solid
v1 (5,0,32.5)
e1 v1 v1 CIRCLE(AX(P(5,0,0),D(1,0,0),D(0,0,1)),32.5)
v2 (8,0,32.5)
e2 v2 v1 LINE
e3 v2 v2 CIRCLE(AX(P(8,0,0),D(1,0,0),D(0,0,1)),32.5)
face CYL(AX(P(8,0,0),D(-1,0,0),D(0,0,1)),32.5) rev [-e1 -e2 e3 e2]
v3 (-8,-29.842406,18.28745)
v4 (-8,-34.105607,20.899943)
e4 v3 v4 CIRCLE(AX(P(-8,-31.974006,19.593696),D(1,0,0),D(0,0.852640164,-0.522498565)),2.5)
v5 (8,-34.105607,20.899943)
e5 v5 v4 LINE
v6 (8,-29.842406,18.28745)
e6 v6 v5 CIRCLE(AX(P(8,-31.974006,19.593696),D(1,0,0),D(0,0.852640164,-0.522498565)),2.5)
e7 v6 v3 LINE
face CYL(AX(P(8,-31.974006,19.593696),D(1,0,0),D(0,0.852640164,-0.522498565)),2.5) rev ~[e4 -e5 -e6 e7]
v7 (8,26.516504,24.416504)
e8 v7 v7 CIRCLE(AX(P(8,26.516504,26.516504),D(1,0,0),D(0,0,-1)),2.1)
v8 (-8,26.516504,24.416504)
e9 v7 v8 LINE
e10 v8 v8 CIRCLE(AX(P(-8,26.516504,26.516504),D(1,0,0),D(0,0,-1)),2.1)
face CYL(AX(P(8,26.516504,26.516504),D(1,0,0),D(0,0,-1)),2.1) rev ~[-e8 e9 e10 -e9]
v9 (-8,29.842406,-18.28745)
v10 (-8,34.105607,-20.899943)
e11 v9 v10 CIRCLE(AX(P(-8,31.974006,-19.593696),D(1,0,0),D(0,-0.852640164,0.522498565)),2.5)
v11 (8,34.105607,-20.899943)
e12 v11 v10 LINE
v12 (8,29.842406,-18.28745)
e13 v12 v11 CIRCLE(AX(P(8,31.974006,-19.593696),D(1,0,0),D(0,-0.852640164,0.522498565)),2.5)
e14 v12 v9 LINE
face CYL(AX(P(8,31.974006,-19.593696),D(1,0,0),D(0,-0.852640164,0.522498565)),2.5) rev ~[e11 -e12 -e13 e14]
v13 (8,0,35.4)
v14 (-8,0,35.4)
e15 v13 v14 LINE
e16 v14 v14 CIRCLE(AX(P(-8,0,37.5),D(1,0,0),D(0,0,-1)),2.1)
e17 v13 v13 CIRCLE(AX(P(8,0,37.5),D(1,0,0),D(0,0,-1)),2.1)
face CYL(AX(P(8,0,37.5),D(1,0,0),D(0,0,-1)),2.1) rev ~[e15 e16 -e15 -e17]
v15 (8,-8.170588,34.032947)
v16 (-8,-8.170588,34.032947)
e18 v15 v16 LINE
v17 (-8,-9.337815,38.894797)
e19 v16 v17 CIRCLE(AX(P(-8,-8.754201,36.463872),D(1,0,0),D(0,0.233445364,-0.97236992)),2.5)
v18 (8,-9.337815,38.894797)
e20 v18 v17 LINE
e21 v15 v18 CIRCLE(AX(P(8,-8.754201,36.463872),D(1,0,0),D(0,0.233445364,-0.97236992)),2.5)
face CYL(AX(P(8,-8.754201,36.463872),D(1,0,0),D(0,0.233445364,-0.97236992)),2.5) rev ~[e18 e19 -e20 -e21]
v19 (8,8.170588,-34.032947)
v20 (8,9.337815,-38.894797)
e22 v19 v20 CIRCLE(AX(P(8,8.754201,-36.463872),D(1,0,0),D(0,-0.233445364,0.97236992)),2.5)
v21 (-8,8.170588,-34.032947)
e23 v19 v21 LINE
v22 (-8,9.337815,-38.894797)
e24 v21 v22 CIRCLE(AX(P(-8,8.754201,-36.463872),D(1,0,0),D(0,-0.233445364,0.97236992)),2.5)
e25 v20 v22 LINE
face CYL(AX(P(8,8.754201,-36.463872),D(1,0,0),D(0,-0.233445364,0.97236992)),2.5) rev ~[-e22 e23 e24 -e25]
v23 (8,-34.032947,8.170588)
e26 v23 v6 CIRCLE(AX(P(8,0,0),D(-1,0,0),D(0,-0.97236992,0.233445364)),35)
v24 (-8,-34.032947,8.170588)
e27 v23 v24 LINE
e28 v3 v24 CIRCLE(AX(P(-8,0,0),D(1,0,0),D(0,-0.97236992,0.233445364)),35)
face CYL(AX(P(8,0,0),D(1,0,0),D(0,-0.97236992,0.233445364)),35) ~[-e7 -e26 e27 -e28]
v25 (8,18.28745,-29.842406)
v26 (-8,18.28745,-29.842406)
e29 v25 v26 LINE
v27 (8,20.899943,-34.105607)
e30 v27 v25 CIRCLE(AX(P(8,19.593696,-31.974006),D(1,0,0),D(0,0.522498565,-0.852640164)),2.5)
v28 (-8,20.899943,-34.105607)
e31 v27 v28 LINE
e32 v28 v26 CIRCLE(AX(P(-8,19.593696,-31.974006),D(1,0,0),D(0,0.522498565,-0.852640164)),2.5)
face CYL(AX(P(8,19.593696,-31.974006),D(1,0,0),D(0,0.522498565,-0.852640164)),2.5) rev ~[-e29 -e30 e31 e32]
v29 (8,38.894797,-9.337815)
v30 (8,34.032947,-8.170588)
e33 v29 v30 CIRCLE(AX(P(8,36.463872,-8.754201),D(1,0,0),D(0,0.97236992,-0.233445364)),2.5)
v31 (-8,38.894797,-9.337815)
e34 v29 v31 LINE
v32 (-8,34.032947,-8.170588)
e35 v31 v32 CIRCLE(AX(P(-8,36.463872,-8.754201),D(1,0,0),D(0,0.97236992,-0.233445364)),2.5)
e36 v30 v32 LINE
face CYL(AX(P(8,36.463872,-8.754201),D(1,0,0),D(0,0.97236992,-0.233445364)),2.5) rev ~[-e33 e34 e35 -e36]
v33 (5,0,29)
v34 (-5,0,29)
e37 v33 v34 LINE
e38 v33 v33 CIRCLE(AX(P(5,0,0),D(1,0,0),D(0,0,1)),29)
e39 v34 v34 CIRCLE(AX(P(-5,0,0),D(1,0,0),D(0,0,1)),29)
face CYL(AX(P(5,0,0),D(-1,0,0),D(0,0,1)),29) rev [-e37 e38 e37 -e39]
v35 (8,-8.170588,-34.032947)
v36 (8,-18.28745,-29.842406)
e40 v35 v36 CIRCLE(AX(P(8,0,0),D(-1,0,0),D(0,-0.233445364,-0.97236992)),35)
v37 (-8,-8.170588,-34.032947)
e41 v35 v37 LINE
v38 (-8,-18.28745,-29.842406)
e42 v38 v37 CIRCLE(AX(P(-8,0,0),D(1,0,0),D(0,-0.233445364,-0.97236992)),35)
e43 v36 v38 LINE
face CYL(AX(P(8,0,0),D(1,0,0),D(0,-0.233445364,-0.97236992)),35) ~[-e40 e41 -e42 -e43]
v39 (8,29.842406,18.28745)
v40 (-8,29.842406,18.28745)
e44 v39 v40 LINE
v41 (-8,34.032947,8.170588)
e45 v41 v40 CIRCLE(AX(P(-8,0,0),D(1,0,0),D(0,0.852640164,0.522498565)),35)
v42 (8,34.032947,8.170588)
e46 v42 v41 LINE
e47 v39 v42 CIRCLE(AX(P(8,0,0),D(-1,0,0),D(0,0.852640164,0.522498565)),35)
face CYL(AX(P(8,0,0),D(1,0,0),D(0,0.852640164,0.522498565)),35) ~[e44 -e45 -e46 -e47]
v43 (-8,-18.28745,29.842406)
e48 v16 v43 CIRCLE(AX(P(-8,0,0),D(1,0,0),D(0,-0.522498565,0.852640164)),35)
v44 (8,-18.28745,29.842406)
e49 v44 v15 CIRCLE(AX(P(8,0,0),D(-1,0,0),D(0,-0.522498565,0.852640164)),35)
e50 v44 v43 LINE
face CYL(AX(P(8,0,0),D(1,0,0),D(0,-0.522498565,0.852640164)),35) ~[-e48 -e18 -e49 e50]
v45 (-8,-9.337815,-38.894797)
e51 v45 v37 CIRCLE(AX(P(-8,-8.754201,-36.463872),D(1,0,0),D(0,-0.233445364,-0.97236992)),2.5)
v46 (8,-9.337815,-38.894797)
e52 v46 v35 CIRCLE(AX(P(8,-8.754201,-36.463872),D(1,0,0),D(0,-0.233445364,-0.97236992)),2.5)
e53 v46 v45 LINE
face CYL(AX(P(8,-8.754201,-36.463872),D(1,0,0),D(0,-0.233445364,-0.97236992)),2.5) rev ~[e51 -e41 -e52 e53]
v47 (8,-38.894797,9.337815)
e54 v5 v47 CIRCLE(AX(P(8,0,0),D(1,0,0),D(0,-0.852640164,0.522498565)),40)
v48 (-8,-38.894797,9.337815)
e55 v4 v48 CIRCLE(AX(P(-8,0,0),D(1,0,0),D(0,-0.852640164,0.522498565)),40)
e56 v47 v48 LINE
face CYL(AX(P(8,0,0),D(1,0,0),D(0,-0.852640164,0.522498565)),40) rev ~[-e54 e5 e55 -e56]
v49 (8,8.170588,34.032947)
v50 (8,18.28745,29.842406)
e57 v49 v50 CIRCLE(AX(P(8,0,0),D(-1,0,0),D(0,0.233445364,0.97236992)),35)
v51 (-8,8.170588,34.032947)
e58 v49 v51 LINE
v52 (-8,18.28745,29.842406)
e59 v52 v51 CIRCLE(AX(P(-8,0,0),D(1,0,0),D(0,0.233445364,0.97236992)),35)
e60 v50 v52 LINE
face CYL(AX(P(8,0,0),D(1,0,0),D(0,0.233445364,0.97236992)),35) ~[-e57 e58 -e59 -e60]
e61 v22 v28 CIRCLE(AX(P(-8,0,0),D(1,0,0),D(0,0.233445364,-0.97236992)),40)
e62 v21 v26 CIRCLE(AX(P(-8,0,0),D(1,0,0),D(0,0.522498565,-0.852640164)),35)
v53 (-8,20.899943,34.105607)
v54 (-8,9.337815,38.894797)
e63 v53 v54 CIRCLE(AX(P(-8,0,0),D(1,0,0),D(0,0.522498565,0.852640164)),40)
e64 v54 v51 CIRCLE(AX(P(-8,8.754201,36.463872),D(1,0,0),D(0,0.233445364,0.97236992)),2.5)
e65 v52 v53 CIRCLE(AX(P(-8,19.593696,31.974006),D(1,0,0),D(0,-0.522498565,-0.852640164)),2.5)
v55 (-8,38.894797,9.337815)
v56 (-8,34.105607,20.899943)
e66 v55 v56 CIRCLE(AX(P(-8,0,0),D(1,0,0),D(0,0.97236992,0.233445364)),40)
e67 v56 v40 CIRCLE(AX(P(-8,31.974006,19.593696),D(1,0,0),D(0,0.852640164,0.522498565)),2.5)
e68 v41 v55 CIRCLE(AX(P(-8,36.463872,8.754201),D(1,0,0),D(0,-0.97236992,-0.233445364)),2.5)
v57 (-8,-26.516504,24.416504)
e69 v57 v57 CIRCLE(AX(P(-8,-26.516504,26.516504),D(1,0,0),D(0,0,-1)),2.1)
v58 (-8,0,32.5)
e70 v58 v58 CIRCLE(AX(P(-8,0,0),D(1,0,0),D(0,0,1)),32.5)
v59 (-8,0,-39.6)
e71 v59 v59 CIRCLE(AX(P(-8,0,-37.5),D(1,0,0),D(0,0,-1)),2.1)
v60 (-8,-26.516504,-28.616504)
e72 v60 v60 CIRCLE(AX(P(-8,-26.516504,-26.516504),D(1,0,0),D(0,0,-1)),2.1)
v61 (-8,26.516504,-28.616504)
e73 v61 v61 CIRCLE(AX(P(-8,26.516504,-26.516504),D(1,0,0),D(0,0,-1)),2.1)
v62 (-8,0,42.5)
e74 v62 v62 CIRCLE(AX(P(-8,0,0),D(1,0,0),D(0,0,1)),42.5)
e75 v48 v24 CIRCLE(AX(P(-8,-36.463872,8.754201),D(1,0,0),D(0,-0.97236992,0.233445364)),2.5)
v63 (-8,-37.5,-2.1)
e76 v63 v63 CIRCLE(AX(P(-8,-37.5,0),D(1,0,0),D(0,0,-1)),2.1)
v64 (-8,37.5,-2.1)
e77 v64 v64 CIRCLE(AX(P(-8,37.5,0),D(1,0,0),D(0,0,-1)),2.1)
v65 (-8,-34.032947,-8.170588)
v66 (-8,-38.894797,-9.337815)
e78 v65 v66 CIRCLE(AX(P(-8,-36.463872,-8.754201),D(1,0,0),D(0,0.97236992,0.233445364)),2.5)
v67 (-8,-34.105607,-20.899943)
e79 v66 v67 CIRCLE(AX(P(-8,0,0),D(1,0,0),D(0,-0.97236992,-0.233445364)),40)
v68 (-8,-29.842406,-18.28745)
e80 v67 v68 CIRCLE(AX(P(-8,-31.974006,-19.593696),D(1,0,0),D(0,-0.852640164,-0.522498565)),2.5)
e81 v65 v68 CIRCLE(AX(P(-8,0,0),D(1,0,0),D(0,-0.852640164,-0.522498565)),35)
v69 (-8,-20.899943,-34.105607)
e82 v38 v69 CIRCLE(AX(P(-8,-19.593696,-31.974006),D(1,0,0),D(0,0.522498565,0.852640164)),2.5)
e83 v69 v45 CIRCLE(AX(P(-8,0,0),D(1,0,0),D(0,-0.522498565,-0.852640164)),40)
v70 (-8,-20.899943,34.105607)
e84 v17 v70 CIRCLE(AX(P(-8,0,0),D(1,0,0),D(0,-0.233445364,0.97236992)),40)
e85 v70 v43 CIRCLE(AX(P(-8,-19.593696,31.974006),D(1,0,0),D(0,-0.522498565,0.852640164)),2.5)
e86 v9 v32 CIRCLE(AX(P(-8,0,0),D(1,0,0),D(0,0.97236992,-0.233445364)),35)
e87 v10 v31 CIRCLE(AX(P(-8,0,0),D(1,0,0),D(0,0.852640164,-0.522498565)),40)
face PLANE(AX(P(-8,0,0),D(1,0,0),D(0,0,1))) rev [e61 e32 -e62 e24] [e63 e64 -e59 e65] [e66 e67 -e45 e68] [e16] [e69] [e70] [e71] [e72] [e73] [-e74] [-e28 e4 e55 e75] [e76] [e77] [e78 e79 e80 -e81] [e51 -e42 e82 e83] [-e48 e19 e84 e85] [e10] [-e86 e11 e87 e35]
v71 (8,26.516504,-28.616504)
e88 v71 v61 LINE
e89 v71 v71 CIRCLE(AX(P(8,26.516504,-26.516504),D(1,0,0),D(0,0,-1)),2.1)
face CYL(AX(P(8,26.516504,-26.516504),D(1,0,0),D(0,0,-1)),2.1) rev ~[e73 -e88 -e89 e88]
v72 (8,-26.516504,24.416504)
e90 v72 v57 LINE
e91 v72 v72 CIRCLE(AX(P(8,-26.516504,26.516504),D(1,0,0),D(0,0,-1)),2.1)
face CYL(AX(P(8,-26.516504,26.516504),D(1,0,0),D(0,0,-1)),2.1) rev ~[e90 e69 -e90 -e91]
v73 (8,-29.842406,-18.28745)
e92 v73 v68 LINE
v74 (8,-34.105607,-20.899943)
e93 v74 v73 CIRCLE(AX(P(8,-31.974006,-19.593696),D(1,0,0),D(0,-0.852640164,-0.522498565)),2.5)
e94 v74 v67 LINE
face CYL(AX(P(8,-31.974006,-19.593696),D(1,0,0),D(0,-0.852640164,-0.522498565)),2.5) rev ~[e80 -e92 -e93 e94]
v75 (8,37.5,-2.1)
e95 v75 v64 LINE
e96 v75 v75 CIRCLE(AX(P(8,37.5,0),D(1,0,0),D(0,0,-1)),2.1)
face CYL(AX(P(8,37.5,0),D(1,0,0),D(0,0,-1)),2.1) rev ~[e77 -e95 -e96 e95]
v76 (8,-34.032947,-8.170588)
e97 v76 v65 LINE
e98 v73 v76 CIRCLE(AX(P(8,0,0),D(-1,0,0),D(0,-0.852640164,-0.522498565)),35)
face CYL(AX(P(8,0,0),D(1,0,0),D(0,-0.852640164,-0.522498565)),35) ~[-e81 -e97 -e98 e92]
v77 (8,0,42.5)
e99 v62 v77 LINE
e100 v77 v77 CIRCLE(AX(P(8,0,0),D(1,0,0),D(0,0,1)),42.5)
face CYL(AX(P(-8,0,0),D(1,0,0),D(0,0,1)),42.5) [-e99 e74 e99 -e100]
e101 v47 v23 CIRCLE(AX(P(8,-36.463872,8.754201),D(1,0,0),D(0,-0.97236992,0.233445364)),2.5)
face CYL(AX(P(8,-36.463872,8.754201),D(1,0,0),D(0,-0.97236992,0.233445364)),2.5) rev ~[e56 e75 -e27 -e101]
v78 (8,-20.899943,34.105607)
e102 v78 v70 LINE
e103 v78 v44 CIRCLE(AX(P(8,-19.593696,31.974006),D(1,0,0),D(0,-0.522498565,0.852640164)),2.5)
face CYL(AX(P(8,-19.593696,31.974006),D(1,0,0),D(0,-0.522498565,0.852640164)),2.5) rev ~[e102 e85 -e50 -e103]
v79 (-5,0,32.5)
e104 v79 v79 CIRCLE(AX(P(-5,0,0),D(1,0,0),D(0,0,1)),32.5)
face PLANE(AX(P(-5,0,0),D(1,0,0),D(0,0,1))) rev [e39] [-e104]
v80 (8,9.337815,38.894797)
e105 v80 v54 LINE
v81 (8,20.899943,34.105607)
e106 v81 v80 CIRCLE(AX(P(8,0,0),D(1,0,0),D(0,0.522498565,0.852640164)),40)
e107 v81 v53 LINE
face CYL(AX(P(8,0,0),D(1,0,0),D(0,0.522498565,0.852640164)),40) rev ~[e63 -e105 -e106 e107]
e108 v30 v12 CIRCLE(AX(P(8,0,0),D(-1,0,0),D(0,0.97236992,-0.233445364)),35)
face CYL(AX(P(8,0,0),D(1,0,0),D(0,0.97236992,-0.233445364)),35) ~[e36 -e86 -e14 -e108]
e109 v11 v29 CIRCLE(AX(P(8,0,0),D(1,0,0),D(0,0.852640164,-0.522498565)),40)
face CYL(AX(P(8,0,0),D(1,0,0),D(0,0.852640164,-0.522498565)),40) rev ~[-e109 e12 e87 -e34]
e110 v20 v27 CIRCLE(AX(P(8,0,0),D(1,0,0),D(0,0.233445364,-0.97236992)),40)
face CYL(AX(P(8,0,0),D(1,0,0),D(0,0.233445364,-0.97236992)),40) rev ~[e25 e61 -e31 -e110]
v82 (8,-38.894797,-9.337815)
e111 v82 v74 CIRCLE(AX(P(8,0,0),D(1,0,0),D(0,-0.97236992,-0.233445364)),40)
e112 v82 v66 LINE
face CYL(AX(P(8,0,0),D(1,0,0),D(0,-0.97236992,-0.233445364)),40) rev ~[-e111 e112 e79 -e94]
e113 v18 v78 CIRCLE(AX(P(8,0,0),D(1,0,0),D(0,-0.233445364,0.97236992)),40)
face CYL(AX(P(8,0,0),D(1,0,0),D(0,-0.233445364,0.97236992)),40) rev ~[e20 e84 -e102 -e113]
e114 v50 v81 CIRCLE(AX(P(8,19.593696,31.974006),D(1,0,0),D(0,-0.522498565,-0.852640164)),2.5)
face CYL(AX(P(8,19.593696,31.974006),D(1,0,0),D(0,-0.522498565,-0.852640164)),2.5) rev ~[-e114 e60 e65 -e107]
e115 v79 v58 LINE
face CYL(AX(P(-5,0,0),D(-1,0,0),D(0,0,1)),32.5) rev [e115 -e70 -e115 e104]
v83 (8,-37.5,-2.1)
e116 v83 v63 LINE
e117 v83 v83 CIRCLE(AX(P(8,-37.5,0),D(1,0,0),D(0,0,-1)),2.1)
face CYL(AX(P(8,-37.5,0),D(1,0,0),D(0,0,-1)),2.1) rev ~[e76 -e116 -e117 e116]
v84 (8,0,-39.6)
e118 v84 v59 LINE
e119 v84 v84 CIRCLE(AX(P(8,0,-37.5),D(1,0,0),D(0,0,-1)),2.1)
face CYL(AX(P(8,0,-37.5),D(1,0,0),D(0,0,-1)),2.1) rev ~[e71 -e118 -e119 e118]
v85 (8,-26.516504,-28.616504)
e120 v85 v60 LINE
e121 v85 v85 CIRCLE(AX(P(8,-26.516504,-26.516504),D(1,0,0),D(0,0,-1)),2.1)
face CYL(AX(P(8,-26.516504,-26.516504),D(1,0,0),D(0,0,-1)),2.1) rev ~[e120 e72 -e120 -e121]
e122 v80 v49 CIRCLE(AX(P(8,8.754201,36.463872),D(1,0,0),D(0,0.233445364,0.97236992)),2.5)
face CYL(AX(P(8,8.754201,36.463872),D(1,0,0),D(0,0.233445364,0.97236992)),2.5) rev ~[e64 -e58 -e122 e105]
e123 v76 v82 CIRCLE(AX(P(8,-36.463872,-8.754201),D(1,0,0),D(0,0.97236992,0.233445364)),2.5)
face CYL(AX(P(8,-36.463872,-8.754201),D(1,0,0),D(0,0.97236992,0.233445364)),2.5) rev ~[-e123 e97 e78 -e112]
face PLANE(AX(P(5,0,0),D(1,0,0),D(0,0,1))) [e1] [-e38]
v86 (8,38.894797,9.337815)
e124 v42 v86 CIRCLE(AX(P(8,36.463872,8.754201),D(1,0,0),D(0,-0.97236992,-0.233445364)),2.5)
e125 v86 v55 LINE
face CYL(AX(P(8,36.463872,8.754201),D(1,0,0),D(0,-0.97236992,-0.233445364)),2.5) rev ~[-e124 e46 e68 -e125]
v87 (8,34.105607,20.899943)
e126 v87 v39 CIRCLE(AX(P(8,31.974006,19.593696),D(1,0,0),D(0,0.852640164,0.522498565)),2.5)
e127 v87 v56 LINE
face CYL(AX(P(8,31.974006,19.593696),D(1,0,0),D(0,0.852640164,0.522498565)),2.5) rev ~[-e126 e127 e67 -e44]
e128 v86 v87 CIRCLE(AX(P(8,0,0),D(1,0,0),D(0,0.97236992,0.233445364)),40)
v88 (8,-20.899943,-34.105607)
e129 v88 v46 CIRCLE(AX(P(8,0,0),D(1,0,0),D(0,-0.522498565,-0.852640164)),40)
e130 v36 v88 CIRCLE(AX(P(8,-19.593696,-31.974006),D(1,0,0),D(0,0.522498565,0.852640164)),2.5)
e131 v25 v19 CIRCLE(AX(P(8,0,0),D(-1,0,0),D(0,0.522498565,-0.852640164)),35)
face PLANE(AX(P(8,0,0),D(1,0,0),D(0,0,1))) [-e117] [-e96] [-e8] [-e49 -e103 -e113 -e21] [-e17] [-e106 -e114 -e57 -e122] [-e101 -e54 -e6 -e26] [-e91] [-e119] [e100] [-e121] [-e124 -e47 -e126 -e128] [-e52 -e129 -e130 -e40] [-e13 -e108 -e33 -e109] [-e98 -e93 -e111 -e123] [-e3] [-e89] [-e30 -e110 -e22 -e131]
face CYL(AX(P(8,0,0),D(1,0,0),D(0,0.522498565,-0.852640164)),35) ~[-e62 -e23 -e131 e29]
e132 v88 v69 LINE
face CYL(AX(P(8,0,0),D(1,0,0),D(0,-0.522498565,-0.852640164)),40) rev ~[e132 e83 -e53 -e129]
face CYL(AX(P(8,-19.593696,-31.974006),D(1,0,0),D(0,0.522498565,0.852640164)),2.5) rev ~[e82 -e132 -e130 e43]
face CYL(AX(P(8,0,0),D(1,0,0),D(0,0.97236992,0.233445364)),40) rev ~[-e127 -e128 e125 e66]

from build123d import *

# Parameters (mm, degrees)
SKETCH_2_R          = 2.1
CUT_EXTRUDE_1_DEPTH = 63.197266821


with BuildPart() as part:
    # 草图1 → 旋转1 (revolve)
    with BuildSketch(Plane(origin=(0, 0, 0), x_dir=(1, 0, 0), z_dir=(0, 1, 0)), mode=Mode.PRIVATE) as revolve_1_sk:
        Polygon((-5, 29), (-5, 32.5), (-8, 32.5), (-8, 42.5), (8, 42.5), (8, 32.5), (5, 32.5), (5, 29), align=None)
    revolve(revolve_1_sk.sketch.rotate(Axis((-880.62625216, 0, 0), (1, 0, 0)), 180), axis=Axis((-880.62625216, 0, 0), (1, 0, 0)))

    # 草图2 → 切除-拉伸1 (cut, through all)
    with BuildSketch(Plane(origin=(8, 0, 0), x_dir=(0, 0, -1), z_dir=(1, 0, 0))):
        with Locations((0, 37.5)):
            Circle(SKETCH_2_R)
        with Locations((26.516504294, 26.516504294)):
            Circle(SKETCH_2_R)
        with Locations((37.5, 0)):
            Circle(SKETCH_2_R)
        with Locations((26.516504294, -26.516504294)):
            Circle(SKETCH_2_R)
        with Locations((0, -37.5)):
            Circle(SKETCH_2_R)
        with Locations((-26.516504294, -26.516504294)):
            Circle(SKETCH_2_R)
        with Locations((-37.5, 0)):
            Circle(SKETCH_2_R)
        with Locations((-26.516504294, 26.516504294)):
            Circle(SKETCH_2_R)
        with BuildLine():
            ThreePointArc((20.899942589, 34.105606574), (15.307337295, 36.9551813), (9.337814554, 38.894796816))
            ThreePointArc((9.337814554, 38.894796816), (6.323276344, 37.047485425), (8.170587735, 34.032947214))
            ThreePointArc((8.170587735, 34.032947214), (13.393920133, 32.335783638), (18.287449765, 29.842405752))
            ThreePointArc((18.287449765, 29.842405752), (21.725296588, 30.667759751), (20.899942589, 34.105606574))
        make_face()
        with BuildLine():
            ThreePointArc((38.894796816, 9.337814554), (36.9551813, 15.307337295), (34.105606574, 20.899942589))
            ThreePointArc((34.105606574, 20.899942589), (30.667759751, 21.725296588), (29.842405752, 18.287449765))
            ThreePointArc((29.842405752, 18.287449765), (32.335783638, 13.393920133), (34.032947214, 8.170587735))
            ThreePointArc((34.032947214, 8.170587735), (37.047485425, 6.323276344), (38.894796816, 9.337814554))
        make_face()
        with BuildLine():
            ThreePointArc((34.105606574, -20.899942589), (36.9551813, -15.307337295), (38.894796816, -9.337814554))
            ThreePointArc((38.894796816, -9.337814554), (37.047485425, -6.323276344), (34.032947214, -8.170587735))
            ThreePointArc((34.032947214, -8.170587735), (32.335783638, -13.393920133), (29.842405752, -18.287449765))
            ThreePointArc((29.842405752, -18.287449765), (30.667759751, -21.725296588), (34.105606574, -20.899942589))
        make_face()
        with BuildLine():
            ThreePointArc((9.337814554, -38.894796816), (15.307337295, -36.9551813), (20.899942589, -34.105606574))
            ThreePointArc((20.899942589, -34.105606574), (21.725296588, -30.667759751), (18.287449765, -29.842405752))
            ThreePointArc((18.287449765, -29.842405752), (13.393920133, -32.335783638), (8.170587735, -34.032947214))
            ThreePointArc((8.170587735, -34.032947214), (6.323276344, -37.047485425), (9.337814554, -38.894796816))
        make_face()
        with BuildLine():
            ThreePointArc((-20.899942589, -34.105606574), (-15.307337295, -36.9551813), (-9.337814554, -38.894796816))
            ThreePointArc((-9.337814554, -38.894796816), (-6.323276344, -37.047485425), (-8.170587735, -34.032947214))
            ThreePointArc((-8.170587735, -34.032947214), (-13.393920133, -32.335783638), (-18.287449765, -29.842405752))
            ThreePointArc((-18.287449765, -29.842405752), (-21.725296588, -30.667759751), (-20.899942589, -34.105606574))
        make_face()
        with BuildLine():
            ThreePointArc((-38.894796816, -9.337814554), (-36.9551813, -15.307337295), (-34.105606574, -20.899942589))
            ThreePointArc((-34.105606574, -20.899942589), (-30.667759751, -21.725296588), (-29.842405752, -18.287449765))
            ThreePointArc((-29.842405752, -18.287449765), (-32.335783638, -13.393920133), (-34.032947214, -8.170587735))
            ThreePointArc((-34.032947214, -8.170587735), (-37.047485425, -6.323276344), (-38.894796816, -9.337814554))
        make_face()
        with BuildLine():
            ThreePointArc((-34.105606574, 20.899942589), (-36.9551813, 15.307337295), (-38.894796816, 9.337814554))
            ThreePointArc((-38.894796816, 9.337814554), (-37.047485425, 6.323276344), (-34.032947214, 8.170587735))
            ThreePointArc((-34.032947214, 8.170587735), (-32.335783638, 13.393920133), (-29.842405752, 18.287449765))
            ThreePointArc((-29.842405752, 18.287449765), (-30.667759751, 21.725296588), (-34.105606574, 20.899942589))
        make_face()
        with BuildLine():
            ThreePointArc((-9.337814554, 38.894796816), (-15.307337295, 36.9551813), (-20.899942589, 34.105606574))
            ThreePointArc((-20.899942589, 34.105606574), (-21.725296588, 30.667759751), (-18.287449765, 29.842405752))
            ThreePointArc((-18.287449765, 29.842405752), (-13.393920133, 32.335783638), (-8.170587735, 34.032947214))
            ThreePointArc((-8.170587735, 34.032947214), (-6.323276344, 37.047485425), (-9.337814554, 38.894796816))
        make_face()
    extrude(amount=-CUT_EXTRUDE_1_DEPTH, mode=Mode.SUBTRACT)


solid = part.part
